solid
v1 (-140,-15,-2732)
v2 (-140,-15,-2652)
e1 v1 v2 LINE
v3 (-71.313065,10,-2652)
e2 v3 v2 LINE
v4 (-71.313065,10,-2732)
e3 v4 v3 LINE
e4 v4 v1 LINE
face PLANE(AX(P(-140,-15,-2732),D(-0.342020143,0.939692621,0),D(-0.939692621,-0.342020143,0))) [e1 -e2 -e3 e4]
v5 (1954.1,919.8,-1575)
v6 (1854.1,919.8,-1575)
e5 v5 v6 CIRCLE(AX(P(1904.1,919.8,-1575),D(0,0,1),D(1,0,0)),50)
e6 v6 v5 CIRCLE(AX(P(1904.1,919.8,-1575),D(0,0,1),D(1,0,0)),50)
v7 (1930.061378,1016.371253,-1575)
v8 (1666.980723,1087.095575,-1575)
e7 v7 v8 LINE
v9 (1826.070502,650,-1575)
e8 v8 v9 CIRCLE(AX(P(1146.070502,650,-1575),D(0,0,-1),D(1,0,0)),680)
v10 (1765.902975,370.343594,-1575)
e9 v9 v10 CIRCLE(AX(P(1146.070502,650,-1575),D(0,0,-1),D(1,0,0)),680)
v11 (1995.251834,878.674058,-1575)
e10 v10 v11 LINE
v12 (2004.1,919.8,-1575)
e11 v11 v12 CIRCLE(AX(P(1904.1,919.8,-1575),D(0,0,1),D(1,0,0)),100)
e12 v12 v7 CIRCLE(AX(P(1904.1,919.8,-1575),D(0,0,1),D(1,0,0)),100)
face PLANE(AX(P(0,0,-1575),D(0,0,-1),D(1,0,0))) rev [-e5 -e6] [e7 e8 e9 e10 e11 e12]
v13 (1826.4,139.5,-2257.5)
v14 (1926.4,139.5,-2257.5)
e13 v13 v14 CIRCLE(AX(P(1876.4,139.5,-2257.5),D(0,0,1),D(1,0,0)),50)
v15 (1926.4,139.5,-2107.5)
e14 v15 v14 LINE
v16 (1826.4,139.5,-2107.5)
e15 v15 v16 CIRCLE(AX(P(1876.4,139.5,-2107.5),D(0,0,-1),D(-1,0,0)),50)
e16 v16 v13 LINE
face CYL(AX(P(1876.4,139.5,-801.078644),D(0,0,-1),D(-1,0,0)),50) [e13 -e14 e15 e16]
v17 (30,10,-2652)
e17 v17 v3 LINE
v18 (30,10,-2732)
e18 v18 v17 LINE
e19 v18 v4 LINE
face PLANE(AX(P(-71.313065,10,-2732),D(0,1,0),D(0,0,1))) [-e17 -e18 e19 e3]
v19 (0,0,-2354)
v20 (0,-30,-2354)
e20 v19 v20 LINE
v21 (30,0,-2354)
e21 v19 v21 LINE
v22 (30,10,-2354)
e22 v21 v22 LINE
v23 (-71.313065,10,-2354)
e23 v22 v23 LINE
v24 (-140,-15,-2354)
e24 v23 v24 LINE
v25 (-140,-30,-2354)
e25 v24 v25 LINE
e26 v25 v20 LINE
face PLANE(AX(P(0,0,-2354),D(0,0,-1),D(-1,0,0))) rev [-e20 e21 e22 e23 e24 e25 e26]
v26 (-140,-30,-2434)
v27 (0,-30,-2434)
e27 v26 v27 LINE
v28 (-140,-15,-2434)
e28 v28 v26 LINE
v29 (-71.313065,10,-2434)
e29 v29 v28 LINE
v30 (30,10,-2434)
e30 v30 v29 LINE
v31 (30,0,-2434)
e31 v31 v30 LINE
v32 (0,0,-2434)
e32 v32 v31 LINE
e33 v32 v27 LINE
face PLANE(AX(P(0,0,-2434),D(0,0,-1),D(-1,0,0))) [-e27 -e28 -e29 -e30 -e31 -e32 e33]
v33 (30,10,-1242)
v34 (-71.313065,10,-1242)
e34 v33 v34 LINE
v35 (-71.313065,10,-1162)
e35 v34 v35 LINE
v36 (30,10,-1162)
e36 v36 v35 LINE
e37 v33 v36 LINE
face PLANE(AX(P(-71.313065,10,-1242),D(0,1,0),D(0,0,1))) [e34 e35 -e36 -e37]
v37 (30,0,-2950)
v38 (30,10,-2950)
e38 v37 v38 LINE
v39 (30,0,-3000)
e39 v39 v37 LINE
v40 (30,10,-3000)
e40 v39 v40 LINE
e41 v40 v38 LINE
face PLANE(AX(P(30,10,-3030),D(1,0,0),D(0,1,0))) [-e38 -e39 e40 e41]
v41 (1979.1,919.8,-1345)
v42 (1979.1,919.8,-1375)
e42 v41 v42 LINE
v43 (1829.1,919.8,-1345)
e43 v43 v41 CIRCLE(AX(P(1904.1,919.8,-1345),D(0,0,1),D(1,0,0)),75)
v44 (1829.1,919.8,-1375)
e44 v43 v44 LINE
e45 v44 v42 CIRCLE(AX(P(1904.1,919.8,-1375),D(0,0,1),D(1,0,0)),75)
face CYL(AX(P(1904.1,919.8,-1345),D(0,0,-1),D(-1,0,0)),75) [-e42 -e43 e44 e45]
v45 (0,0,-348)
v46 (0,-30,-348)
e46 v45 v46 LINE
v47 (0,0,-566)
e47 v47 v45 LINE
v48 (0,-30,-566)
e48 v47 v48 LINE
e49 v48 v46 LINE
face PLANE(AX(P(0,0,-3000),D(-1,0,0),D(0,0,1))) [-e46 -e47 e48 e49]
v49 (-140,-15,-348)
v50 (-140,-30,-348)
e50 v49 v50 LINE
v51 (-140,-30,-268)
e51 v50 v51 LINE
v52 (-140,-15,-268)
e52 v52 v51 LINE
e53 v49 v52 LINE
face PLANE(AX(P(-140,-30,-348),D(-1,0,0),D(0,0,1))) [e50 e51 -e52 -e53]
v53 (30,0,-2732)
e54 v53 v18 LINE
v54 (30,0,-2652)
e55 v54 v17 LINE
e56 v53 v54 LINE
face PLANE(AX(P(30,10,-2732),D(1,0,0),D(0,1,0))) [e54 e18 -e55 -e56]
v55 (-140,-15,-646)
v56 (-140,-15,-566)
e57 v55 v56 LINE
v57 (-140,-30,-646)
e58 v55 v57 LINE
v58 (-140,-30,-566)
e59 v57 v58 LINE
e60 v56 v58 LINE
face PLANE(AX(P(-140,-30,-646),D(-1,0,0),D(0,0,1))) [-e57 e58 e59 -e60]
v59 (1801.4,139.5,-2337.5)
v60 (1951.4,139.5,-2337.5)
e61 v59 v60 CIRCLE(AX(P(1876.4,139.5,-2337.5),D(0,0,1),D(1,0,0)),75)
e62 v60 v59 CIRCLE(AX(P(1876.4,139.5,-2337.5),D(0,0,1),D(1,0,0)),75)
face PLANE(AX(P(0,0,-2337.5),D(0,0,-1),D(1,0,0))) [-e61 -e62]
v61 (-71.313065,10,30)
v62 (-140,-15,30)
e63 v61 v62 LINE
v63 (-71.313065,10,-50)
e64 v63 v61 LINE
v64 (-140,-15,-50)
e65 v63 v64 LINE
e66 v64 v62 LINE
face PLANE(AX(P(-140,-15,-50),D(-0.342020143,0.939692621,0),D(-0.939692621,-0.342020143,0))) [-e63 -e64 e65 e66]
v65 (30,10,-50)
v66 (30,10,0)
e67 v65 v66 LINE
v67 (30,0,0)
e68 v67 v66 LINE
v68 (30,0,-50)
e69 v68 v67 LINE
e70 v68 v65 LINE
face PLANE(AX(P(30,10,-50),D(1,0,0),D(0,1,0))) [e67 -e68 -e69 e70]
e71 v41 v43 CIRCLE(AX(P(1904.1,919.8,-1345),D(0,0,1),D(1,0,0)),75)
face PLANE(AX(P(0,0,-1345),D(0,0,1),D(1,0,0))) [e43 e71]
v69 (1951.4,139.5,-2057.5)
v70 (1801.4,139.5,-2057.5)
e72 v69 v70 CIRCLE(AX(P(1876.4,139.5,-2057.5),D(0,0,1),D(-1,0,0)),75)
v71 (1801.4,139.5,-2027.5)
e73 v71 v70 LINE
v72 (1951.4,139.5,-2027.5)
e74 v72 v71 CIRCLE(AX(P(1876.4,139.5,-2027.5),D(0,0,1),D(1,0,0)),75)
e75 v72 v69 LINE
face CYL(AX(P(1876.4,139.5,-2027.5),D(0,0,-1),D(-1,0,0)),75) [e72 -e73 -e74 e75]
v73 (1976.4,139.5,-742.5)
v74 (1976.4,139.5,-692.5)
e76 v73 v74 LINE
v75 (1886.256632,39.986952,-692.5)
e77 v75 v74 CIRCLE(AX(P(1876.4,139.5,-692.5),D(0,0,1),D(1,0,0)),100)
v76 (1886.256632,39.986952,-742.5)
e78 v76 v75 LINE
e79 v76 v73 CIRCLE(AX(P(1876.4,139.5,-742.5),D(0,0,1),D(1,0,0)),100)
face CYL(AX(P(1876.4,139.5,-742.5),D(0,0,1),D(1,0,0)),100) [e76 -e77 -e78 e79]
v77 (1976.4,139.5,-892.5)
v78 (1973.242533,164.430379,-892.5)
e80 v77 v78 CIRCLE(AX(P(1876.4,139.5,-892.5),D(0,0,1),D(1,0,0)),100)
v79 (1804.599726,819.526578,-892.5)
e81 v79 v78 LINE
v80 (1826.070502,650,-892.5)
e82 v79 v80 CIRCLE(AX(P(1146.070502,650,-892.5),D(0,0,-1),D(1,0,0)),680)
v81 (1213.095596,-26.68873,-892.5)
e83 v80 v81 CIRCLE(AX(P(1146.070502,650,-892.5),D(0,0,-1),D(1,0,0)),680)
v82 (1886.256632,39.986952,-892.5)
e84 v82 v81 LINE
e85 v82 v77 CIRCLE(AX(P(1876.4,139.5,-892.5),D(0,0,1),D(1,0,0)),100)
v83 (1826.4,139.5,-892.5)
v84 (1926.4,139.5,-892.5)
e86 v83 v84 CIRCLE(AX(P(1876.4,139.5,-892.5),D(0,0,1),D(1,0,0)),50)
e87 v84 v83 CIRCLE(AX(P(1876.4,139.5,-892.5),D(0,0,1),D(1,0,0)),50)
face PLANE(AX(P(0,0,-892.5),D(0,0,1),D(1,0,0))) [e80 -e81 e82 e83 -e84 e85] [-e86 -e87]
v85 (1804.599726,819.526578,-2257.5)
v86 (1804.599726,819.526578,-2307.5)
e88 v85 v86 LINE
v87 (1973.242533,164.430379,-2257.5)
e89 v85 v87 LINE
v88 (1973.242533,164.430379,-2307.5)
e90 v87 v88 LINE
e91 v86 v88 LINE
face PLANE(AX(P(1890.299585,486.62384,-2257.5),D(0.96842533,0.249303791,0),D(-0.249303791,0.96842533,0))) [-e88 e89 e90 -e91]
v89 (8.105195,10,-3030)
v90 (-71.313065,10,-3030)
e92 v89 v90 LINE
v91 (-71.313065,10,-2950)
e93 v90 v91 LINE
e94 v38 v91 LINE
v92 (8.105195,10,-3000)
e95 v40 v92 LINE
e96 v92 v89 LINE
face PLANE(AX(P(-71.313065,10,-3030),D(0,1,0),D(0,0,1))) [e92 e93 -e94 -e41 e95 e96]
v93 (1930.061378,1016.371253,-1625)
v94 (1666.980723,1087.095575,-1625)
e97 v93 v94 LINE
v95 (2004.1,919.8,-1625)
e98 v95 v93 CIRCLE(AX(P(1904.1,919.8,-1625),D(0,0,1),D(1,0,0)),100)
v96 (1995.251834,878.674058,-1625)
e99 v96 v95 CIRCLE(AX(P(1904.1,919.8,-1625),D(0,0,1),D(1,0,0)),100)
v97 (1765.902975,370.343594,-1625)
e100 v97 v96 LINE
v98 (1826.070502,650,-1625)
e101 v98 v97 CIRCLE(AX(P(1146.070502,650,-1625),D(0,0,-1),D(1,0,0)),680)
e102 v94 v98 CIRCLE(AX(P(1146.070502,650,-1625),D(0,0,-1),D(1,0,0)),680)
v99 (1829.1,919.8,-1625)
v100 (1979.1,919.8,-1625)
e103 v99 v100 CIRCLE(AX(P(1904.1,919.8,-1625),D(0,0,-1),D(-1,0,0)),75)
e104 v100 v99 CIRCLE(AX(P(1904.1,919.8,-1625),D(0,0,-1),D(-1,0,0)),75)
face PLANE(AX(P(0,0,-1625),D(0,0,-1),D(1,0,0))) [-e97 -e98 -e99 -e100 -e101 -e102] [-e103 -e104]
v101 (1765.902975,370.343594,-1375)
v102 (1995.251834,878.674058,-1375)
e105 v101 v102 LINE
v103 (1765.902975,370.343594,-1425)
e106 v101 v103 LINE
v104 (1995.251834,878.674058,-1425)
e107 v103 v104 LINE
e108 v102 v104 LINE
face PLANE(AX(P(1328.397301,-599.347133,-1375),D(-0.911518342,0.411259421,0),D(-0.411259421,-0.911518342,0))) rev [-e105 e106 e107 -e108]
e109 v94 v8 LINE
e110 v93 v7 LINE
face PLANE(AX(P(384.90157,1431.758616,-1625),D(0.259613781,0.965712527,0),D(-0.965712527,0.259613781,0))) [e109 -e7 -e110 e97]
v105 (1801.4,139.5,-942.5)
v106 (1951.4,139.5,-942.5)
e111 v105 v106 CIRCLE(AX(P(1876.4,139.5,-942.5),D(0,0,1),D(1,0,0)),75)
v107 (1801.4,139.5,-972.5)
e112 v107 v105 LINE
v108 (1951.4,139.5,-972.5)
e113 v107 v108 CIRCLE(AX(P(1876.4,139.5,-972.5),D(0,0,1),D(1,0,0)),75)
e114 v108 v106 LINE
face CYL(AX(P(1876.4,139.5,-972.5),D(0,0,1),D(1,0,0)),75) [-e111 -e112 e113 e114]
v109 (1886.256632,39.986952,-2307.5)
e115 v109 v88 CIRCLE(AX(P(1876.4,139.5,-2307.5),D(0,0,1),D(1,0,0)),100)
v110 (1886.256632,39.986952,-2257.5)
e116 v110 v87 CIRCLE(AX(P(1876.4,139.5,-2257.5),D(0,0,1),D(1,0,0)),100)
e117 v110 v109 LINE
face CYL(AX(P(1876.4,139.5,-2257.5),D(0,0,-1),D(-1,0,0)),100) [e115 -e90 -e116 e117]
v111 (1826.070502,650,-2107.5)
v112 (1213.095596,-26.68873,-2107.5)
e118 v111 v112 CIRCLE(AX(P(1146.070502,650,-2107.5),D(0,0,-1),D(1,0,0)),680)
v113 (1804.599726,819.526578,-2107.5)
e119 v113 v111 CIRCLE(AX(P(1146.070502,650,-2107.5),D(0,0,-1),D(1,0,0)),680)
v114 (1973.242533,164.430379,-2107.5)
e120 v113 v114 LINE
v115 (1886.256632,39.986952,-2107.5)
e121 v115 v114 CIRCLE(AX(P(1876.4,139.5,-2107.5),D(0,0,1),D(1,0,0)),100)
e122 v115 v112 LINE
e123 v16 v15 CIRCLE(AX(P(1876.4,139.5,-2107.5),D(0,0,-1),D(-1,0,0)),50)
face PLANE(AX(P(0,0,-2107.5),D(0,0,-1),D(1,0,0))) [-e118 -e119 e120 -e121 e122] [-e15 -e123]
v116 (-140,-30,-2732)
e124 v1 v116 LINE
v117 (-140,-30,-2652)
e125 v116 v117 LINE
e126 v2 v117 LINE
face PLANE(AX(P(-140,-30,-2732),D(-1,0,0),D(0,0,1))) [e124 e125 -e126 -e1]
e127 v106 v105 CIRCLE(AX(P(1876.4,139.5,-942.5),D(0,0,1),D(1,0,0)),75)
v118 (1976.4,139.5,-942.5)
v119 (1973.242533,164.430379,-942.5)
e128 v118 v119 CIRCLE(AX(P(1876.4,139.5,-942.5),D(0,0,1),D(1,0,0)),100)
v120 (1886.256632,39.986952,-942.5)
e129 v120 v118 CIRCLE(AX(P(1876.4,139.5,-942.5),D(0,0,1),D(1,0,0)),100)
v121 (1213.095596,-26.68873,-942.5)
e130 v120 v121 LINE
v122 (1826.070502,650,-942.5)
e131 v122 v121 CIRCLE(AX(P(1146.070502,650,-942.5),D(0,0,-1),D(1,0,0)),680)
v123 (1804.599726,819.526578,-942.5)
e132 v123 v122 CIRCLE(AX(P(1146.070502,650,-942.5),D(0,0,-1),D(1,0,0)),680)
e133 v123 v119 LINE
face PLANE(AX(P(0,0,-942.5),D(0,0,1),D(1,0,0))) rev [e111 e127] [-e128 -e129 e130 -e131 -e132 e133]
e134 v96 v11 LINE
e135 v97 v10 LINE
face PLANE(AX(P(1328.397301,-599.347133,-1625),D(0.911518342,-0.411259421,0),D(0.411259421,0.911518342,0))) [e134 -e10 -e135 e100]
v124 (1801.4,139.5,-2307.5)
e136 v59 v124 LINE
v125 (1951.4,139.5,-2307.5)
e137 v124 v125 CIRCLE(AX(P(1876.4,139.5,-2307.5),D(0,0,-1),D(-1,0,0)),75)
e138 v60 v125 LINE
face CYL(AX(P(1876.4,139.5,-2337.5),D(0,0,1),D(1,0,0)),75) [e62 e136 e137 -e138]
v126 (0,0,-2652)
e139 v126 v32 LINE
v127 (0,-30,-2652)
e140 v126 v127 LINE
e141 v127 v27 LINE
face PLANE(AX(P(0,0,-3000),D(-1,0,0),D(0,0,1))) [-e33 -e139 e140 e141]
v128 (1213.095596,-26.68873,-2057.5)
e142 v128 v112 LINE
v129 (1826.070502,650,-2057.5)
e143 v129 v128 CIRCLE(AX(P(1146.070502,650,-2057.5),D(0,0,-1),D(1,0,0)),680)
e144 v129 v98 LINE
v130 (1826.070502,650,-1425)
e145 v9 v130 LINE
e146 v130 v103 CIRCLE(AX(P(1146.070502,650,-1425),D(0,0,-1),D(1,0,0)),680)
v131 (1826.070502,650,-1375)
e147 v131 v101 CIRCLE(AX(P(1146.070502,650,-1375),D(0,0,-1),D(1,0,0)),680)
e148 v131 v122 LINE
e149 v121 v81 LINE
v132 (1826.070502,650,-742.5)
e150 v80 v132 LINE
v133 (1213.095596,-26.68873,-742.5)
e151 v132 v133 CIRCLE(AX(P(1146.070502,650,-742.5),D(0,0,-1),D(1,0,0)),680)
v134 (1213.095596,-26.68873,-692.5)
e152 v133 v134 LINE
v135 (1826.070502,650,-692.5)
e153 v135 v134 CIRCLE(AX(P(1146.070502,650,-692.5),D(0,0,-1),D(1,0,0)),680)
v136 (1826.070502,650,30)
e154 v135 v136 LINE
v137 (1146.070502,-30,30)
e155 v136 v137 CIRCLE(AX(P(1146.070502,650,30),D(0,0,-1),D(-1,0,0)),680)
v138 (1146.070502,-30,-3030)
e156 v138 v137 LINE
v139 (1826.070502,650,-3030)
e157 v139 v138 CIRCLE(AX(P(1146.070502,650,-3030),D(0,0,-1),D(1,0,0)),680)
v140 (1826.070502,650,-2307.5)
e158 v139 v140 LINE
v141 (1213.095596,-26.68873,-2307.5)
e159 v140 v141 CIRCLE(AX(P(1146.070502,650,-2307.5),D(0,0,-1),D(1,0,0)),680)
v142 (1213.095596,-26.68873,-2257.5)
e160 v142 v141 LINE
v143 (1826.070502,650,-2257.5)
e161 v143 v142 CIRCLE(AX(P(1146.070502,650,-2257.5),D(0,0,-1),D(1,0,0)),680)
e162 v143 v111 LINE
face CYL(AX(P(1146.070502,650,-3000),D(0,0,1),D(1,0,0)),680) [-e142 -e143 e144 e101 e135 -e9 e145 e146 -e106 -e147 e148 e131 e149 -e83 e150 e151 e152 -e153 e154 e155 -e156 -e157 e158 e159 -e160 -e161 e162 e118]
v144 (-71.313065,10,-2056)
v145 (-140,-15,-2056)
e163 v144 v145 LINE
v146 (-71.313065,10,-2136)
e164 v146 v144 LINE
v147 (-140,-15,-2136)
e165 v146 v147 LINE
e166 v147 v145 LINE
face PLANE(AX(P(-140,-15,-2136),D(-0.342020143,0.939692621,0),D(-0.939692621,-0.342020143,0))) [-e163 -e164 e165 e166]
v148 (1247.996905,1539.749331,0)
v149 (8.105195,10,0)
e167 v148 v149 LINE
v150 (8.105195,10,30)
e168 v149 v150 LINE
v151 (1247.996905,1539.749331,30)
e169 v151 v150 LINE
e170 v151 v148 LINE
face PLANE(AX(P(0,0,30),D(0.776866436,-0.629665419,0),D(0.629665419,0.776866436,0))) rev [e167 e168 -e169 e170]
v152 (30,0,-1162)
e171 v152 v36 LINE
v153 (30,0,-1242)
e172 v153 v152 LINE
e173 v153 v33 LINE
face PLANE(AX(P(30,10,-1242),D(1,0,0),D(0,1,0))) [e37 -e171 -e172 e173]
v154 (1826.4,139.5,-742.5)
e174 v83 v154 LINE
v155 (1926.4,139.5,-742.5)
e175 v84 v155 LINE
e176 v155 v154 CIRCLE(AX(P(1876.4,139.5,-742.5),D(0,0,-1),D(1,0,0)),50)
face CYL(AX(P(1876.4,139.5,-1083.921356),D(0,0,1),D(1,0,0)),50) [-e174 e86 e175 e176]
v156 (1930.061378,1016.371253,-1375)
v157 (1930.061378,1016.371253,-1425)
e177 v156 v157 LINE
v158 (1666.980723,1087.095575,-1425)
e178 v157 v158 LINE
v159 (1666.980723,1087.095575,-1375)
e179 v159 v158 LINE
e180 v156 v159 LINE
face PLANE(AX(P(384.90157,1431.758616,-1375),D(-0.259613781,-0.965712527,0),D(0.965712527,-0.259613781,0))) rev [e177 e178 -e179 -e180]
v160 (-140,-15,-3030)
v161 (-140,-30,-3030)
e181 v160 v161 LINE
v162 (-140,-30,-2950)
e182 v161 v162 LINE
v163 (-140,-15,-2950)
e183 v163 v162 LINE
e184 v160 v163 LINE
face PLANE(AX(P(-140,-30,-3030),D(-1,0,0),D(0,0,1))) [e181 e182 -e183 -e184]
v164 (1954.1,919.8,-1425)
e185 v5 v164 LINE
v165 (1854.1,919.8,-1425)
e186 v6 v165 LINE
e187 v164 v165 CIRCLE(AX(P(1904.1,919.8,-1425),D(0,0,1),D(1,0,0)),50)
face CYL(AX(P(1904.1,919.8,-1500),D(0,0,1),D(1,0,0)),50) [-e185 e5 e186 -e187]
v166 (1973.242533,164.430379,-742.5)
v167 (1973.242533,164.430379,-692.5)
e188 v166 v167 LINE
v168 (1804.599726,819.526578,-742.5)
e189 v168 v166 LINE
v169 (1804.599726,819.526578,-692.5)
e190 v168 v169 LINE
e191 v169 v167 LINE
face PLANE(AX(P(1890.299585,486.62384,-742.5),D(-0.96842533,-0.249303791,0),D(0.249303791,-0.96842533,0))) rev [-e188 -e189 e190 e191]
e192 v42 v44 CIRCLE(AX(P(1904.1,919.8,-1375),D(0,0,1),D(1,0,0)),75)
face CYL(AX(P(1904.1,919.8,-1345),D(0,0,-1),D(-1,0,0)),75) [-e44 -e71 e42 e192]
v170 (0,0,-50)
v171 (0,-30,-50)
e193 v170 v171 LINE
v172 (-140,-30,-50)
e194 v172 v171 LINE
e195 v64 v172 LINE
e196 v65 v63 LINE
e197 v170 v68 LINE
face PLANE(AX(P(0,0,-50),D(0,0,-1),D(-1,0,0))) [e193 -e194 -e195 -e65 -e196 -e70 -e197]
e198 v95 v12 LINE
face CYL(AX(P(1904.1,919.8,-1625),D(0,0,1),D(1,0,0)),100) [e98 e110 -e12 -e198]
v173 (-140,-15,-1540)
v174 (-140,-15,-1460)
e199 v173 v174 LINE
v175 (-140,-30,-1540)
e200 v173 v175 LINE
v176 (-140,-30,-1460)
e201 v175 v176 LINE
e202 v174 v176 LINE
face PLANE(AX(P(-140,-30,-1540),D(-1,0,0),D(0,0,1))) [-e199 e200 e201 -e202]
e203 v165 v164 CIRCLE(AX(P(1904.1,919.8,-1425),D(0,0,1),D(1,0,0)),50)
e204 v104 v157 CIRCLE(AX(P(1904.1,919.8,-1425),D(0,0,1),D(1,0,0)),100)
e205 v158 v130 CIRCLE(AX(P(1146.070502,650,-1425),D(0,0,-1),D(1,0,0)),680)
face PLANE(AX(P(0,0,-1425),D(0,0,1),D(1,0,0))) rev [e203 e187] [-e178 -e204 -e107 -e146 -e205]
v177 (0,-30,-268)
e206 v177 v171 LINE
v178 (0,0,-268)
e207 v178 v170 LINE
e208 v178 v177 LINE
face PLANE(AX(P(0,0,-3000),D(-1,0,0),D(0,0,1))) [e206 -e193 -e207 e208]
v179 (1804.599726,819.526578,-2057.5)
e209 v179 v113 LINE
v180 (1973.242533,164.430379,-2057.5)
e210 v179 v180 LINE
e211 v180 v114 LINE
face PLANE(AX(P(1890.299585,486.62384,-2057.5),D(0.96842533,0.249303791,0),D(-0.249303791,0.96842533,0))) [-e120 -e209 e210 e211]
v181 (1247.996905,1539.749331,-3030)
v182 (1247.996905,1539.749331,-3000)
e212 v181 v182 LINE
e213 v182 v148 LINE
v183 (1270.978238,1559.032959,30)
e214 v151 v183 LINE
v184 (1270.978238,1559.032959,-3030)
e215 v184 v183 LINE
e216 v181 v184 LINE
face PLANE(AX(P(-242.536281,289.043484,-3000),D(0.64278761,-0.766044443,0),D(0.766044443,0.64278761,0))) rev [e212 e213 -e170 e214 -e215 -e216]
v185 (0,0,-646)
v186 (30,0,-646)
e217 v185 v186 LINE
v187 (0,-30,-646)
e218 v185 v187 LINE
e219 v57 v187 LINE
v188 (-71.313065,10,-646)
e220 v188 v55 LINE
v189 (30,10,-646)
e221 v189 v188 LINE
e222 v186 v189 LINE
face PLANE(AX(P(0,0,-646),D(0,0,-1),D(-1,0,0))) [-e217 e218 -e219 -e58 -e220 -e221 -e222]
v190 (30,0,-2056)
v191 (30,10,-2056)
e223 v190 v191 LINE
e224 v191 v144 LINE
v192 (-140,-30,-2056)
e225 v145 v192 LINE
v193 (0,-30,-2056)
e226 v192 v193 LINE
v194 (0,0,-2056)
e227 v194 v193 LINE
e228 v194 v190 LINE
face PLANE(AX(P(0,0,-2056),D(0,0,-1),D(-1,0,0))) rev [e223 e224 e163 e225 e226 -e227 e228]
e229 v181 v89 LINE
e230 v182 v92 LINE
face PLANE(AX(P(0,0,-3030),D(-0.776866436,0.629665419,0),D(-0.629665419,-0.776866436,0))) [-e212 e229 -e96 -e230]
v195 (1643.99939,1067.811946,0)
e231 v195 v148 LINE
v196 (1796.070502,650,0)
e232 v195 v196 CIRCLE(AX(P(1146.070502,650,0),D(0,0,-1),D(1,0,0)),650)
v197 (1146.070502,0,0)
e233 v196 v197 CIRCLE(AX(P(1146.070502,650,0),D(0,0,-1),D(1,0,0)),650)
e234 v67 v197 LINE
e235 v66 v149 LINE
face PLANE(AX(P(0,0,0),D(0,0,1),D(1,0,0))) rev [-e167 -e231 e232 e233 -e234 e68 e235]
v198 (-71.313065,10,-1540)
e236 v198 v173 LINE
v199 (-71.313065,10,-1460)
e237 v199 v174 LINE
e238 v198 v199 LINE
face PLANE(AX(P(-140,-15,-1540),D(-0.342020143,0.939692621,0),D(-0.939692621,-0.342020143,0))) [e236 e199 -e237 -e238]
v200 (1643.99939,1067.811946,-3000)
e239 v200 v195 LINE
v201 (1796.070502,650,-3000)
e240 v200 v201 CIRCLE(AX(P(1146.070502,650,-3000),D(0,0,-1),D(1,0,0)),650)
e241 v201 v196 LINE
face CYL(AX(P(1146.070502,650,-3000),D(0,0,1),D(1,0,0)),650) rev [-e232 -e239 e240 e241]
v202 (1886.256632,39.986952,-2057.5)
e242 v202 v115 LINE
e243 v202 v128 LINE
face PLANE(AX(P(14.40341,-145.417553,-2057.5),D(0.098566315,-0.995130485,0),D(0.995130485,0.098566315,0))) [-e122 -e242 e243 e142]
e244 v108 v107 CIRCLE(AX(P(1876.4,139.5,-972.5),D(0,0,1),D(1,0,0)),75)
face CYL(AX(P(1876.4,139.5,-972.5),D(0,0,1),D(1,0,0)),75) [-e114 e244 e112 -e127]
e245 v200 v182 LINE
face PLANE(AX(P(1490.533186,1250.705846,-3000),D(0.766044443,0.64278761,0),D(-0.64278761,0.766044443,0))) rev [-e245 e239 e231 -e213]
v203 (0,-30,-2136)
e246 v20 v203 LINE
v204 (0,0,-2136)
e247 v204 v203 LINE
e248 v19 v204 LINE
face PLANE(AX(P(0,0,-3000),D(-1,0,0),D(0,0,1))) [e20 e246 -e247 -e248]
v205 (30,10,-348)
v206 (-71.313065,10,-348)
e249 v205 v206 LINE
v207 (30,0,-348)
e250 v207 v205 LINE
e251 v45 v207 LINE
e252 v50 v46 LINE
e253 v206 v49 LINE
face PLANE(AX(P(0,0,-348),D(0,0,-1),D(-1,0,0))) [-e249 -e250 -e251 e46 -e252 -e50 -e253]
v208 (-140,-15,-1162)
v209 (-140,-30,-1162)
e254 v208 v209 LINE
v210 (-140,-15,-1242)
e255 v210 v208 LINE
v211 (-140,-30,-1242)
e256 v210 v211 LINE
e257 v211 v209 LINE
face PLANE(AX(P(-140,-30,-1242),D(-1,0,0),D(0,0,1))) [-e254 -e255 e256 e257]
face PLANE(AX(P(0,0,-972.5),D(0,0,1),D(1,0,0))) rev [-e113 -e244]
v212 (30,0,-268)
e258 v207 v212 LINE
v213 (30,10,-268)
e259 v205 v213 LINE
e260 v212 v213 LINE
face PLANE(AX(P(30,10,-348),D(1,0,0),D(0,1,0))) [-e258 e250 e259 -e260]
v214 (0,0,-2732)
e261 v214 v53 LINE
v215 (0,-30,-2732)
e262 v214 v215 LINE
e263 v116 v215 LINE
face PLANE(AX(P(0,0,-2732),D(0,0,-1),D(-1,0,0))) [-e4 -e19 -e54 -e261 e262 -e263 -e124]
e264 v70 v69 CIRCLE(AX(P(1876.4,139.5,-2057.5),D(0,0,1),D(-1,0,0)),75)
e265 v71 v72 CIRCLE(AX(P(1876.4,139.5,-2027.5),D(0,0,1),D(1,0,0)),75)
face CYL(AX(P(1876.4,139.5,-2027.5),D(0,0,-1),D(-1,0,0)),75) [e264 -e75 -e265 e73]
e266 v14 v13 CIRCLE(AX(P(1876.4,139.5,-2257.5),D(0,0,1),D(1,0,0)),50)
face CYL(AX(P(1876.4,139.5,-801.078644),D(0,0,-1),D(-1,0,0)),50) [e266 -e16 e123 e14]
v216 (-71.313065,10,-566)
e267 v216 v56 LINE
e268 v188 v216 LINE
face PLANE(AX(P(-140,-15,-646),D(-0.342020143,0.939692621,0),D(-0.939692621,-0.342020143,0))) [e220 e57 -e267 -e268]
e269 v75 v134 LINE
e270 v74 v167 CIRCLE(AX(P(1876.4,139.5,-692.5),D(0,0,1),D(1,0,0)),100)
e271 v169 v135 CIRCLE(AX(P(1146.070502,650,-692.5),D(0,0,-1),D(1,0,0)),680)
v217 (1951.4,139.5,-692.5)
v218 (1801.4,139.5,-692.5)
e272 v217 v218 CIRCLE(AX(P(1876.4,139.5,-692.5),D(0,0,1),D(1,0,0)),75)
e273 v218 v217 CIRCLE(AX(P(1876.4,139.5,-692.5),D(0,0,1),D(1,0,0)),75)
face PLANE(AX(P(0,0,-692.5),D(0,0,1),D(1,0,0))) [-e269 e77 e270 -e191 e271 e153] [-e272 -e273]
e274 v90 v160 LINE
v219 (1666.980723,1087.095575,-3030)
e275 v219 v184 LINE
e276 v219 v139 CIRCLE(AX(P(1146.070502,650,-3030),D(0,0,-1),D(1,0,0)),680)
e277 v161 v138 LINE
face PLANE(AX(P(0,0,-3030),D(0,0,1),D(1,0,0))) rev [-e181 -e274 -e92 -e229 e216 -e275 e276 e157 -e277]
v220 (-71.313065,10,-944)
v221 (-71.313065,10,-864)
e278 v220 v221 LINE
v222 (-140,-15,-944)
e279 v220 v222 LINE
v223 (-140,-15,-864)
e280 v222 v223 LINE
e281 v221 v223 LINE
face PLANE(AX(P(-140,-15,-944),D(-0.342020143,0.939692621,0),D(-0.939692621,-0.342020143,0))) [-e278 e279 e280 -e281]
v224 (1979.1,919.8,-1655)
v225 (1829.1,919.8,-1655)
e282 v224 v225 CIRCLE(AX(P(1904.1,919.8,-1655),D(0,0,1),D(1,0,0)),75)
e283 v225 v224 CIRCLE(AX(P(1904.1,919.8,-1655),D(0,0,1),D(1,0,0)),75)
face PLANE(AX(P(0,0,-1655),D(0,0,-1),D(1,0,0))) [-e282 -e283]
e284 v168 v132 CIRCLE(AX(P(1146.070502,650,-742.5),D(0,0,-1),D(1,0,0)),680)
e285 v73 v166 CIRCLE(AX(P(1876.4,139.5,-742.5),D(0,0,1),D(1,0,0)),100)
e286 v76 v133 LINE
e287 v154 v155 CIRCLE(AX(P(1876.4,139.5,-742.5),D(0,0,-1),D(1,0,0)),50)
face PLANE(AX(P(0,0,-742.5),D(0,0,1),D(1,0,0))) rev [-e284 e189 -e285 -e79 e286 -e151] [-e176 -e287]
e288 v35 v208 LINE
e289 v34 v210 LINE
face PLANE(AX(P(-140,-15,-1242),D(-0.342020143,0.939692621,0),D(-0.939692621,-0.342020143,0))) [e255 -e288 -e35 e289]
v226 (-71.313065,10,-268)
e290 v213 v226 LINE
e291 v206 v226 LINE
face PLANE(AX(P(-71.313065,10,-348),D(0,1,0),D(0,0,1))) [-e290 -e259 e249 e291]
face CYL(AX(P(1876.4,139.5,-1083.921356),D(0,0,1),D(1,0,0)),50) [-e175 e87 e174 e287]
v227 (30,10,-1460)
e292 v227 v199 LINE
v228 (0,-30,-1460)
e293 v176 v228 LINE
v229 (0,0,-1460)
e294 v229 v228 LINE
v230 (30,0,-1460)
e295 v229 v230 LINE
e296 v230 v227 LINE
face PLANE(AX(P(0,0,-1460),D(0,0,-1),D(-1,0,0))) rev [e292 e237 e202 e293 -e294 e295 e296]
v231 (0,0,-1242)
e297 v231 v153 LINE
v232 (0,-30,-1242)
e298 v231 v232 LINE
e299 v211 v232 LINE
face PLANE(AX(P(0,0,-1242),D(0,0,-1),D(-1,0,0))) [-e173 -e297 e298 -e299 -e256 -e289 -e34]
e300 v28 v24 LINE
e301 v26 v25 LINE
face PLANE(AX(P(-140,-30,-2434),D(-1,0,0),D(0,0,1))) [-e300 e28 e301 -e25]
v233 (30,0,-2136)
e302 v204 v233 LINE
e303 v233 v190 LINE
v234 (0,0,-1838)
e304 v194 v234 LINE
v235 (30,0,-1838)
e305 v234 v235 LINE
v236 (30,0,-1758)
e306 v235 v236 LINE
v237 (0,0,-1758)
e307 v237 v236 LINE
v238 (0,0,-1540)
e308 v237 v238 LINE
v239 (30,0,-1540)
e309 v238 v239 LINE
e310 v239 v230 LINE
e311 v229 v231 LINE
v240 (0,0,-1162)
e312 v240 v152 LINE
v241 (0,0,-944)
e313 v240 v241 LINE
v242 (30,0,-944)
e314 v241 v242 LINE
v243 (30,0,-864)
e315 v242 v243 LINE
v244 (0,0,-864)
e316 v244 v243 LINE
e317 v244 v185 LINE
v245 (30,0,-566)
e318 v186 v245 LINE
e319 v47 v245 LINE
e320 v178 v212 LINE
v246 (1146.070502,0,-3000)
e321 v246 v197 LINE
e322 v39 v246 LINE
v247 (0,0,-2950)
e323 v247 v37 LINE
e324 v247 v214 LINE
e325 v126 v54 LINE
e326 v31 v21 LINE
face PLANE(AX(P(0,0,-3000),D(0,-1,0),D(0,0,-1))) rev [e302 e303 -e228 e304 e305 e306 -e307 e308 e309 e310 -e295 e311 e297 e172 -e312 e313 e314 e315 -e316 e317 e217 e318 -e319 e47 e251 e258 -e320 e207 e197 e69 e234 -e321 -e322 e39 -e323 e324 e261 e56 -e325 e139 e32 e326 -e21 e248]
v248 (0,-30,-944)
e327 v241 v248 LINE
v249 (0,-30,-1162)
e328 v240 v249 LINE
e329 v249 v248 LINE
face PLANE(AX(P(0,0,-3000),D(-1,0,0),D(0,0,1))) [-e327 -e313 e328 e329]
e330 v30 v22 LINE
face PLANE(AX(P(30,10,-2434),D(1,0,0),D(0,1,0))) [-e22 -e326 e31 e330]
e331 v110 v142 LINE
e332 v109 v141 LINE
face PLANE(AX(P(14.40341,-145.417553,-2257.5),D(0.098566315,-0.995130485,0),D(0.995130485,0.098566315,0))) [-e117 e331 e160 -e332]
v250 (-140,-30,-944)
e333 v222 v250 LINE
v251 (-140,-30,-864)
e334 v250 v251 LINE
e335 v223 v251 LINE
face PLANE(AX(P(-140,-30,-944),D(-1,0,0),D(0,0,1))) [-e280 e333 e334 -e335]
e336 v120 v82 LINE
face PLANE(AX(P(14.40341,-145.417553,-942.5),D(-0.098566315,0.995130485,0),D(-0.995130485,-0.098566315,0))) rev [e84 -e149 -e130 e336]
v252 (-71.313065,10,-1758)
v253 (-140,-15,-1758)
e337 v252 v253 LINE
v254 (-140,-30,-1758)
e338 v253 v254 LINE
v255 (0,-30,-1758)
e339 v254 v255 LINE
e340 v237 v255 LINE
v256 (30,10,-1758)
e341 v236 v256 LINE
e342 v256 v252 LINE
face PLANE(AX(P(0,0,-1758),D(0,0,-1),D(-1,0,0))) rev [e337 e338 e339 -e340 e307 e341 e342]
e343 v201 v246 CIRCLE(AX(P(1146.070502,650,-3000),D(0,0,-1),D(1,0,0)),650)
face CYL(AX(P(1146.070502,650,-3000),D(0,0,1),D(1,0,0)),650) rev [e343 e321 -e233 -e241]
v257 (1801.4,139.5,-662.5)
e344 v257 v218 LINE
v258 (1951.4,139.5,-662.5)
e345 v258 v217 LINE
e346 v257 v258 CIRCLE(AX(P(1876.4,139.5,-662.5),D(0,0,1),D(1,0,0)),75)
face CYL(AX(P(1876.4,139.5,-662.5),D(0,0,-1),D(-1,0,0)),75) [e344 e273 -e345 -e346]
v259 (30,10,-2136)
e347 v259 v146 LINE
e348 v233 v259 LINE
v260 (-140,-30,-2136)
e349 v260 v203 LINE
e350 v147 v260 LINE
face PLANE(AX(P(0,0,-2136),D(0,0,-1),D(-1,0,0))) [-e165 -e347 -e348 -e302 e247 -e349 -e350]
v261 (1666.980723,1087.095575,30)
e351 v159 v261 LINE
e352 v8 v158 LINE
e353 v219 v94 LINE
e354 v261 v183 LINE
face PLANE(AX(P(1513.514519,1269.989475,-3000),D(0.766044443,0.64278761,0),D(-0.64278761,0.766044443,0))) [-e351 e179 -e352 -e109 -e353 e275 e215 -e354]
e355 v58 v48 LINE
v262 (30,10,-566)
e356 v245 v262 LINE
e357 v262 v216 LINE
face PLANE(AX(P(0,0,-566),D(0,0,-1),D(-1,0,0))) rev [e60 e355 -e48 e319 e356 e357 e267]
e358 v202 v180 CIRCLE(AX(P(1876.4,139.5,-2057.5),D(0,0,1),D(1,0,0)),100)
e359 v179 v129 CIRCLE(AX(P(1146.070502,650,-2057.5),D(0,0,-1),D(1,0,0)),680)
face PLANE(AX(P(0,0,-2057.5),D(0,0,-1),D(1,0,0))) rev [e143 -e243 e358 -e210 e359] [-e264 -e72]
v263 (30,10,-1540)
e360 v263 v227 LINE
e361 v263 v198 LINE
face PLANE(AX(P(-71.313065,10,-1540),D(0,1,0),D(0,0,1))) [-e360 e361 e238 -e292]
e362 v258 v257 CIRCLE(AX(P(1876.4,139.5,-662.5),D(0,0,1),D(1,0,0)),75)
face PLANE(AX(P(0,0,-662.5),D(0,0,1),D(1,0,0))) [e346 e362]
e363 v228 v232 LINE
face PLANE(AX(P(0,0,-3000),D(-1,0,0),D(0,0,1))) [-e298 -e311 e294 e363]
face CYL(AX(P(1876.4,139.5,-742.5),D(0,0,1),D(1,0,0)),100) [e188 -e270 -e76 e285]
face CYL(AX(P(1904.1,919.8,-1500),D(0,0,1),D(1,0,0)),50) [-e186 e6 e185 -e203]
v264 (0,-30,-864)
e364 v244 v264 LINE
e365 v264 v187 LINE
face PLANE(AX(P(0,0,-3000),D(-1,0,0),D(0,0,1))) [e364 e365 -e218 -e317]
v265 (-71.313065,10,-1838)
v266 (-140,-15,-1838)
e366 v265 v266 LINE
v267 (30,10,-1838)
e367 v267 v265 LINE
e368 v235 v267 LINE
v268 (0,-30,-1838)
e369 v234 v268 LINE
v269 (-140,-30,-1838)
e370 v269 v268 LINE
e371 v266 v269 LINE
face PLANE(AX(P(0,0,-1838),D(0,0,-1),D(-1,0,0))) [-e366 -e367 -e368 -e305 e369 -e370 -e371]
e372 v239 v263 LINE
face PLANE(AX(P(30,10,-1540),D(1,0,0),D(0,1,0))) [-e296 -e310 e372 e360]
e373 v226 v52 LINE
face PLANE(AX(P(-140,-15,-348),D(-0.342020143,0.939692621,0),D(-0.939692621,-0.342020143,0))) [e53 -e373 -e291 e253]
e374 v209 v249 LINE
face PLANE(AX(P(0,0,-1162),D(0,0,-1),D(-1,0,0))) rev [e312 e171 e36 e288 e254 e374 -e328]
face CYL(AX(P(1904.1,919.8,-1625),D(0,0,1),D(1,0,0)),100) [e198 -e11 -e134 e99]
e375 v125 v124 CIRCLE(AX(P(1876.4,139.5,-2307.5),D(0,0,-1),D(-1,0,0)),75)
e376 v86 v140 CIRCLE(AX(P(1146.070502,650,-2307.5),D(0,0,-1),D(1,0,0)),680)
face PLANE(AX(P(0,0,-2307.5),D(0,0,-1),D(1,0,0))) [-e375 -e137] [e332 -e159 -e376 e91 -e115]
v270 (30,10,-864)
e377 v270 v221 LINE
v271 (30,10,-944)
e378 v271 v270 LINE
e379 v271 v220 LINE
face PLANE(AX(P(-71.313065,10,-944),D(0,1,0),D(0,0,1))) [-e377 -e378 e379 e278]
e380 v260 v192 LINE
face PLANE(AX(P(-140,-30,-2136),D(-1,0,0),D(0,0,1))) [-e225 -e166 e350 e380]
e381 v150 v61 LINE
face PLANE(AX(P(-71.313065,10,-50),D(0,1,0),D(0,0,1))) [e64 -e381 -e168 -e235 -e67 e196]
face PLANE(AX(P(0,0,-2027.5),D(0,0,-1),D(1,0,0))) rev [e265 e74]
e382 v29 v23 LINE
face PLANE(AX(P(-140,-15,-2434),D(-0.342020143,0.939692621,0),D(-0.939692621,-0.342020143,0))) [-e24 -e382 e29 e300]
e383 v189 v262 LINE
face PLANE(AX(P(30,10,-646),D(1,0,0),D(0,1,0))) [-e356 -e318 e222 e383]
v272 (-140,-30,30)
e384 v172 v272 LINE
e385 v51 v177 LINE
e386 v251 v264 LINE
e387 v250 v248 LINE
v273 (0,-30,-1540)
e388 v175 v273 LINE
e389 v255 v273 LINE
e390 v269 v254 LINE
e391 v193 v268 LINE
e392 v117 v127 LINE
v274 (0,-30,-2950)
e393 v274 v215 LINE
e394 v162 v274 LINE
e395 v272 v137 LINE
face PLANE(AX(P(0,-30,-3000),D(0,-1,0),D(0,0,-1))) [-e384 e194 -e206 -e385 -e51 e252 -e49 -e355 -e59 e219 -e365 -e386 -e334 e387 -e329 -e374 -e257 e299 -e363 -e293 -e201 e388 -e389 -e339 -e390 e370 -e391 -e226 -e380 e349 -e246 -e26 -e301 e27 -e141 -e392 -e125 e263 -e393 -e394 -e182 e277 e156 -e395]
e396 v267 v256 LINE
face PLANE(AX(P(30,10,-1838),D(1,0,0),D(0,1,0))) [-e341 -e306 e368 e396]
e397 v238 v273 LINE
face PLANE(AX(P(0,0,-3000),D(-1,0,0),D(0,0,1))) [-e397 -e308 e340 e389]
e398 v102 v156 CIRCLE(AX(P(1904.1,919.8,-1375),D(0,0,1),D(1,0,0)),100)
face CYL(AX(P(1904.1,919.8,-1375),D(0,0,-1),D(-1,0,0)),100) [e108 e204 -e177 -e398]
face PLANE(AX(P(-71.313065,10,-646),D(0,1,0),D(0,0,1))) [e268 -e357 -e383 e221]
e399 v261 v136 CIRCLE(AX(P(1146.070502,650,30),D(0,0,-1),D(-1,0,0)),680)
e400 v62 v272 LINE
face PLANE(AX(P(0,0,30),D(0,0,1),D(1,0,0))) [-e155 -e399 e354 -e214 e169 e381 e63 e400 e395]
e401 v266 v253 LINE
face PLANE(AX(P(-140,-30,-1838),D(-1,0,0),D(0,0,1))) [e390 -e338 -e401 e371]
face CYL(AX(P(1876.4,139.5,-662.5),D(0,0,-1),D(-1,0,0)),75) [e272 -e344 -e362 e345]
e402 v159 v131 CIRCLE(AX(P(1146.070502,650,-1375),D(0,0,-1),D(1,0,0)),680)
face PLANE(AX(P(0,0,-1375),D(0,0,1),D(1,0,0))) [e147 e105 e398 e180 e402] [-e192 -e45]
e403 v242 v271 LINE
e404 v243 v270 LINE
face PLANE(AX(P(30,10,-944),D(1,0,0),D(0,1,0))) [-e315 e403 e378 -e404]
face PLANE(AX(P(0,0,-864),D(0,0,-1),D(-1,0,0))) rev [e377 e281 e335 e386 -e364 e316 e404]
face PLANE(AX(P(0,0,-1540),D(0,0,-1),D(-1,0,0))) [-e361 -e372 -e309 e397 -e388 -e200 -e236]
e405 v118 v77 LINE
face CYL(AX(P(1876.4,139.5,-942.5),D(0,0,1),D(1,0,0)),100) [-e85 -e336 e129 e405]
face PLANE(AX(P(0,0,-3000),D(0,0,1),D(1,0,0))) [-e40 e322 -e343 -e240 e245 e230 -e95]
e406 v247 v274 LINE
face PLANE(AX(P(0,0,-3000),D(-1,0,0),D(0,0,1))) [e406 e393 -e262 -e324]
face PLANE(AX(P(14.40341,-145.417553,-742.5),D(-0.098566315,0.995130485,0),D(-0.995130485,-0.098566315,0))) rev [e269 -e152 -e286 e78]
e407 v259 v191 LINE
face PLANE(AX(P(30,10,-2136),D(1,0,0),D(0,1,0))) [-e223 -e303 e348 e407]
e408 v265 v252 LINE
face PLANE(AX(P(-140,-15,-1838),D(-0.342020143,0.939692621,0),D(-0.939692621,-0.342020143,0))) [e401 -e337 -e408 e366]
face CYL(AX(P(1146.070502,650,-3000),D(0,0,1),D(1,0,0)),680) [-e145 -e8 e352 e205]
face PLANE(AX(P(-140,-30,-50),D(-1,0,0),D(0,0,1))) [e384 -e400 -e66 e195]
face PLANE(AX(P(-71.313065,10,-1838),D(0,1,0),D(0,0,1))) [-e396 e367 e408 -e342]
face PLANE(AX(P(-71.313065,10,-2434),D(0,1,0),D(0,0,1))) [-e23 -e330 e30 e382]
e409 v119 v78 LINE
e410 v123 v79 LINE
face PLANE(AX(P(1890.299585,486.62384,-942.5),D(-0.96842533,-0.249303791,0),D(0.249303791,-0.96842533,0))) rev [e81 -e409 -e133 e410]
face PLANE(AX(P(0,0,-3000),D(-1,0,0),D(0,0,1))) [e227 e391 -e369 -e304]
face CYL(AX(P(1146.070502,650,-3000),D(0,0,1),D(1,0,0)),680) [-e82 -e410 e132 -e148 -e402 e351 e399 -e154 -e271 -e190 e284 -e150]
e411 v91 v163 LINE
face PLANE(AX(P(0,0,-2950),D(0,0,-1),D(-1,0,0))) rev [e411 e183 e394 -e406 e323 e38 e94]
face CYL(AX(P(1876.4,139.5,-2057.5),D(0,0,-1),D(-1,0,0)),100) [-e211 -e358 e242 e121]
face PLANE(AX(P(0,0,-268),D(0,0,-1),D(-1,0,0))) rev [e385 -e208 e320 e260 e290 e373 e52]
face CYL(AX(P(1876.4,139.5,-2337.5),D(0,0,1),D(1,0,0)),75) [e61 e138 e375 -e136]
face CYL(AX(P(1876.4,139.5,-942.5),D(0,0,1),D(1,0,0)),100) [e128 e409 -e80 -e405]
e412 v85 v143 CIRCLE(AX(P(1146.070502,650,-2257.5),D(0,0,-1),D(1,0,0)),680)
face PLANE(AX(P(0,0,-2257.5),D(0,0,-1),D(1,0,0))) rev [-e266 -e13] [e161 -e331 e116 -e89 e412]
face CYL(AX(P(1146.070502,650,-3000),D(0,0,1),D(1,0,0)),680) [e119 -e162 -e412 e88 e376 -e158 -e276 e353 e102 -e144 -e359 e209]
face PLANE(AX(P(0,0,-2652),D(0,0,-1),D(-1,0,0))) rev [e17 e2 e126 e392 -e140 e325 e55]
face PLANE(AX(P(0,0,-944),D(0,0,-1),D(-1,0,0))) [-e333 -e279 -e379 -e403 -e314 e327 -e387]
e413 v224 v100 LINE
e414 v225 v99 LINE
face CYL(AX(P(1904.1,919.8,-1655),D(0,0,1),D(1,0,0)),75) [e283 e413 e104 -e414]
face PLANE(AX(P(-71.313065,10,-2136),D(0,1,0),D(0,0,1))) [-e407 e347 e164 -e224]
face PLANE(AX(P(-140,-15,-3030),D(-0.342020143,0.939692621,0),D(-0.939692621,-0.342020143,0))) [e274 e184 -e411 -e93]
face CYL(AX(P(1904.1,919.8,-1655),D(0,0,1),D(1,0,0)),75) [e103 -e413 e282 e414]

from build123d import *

# Parameters (mm, degrees)
BOSS_EXTRUDE1_DEPTH  = 3000
BOSS_EXTRUDE2_START  = 30
BOSS_EXTRUDE2_DEPTH  = 30
BOSS_EXTRUDE4_START  = -3000
BOSS_EXTRUDE4_DEPTH  = 30
BOSS_EXTRUDE5_START  = -692.5
SKETCH_1_11_R        = 50
BOSS_EXTRUDE5_DEPTH  = 50
BOSS_EXTRUDE6_START  = -892.5
SKETCH_1_12_R        = 50
BOSS_EXTRUDE6_DEPTH  = 50
BOSS_EXTRUDE7_START  = -1375
SKETCH_1_13_2_R      = 50
BOSS_EXTRUDE7_DEPTH  = 50
SKETCH_3_5_R         = 50
BOSS_EXTRUDE8_DEPTH  = 250
BOSS_EXTRUDE9_START  = 30
SKETCH_3_4_R         = 75
SKETCH_3_4_R_2       = 50
BOSS_EXTRUDE9_DEPTH  = 30
BOSS_EXTRUDE10_START = -250
SKETCH_3_5_2_R       = 75
SKETCH_3_5_2_R_2     = 50
BOSS_EXTRUDE10_DEPTH = 30
BOSS_EXTRUDE11_START = 30
SKETCH_4_3_R         = 75
SKETCH_4_3_R_2       = 50
BOSS_EXTRUDE11_DEPTH = 30
SKETCH_4_3_2_R       = 50
BOSS_EXTRUDE12_DEPTH = 125
BOSS_EXTRUDE13_DEPTH = 80
LPATTERN1_COUNT      = 11
LPATTERN1_PITCH      = 298


with BuildPart() as part:
    # Sketch 1_13 → Boss-Extrude1 (new body)
    with BuildSketch(Plane.XY):
        with BuildLine():
            ThreePointArc((1666.98072299, 1087.095574587), (1762.359796854, 362.619582016), (1146.070501669, -30))
            Line((1146.070501669, -30), (0, -30))
            Line((0, -30), (0, 0))
            Line((0, 0), (1146.070501669, 0))
            ThreePointArc((1146.070501669, 0), (1735.170563243, 375.298129869), (1643.999389696, 1067.811946296))
            Line((1643.999389696, 1067.811946296), (1247.99690453, 1539.749330669))
            Line((1247.99690453, 1539.749330669), (1270.978237824, 1559.03295896))
            Line((1270.978237824, 1559.03295896), (1666.98072299, 1087.095574587))
        make_face()
    extrude(amount=-BOSS_EXTRUDE1_DEPTH)

    # 草图1<7> → Boss-Extrude2 (add)
    with BuildSketch(Plane.XY.offset(BOSS_EXTRUDE2_START)):
        with BuildLine():
            Line((1247.99690453, 1539.749330669), (0, 0))
            Line((0, 0), (0, -30))
            Line((0, -30), (1146.070501669, -30))
            ThreePointArc((1146.070501669, -30), (1762.359796854, 362.619582016), (1666.98072299, 1087.095574587))
            Line((1666.98072299, 1087.095574587), (1270.978237824, 1559.03295896))
            Line((1270.978237824, 1559.03295896), (1247.99690453, 1539.749330669))
        make_face()
    extrude(amount=-BOSS_EXTRUDE2_DEPTH)

    # 草图1<9> → Boss-Extrude4 (add)
    with BuildSketch(Plane.XY.offset(BOSS_EXTRUDE4_START)):
        with BuildLine():
            ThreePointArc((1643.999389696, 1067.811946296), (1735.170563243, 375.298129869), (1146.070501669, 0))
            Line((1146.070501669, 0), (0, 0))
            Line((0, 0), (1247.99690453, 1539.749330669))
            Line((1247.99690453, 1539.749330669), (1643.999389696, 1067.811946296))
        make_face()
        with BuildLine():
            ThreePointArc((1666.98072299, 1087.095574587), (1762.359796854, 362.619582016), (1146.070501669, -30))
            Line((1146.070501669, -30), (0, -30))
            Line((0, -30), (0, 0))
            Line((0, 0), (1146.070501669, 0))
            ThreePointArc((1146.070501669, 0), (1735.170563243, 375.298129869), (1643.999389696, 1067.811946296))
            Line((1643.999389696, 1067.811946296), (1247.99690453, 1539.749330669))
            Line((1247.99690453, 1539.749330669), (1270.978237824, 1559.03295896))
            Line((1270.978237824, 1559.03295896), (1666.98072299, 1087.095574587))
        make_face()
    extrude(amount=-BOSS_EXTRUDE4_DEPTH)

    # 草图1<11> → Boss-Extrude5 (add)
    with BuildSketch(Plane.XY.offset(BOSS_EXTRUDE5_START)):
        with BuildLine():
            Line((1213.095596051, -26.688729567), (1886.256631527, 39.986951534))
            ThreePointArc((1886.256631527, 39.986951534), (1958.361695899, 82.208810404), (1973.242532996, 164.430379118))
            Line((1973.242532996, 164.430379118), (1804.599726039, 819.526578004))
            ThreePointArc((1804.599726039, 819.526578004), (1703.410033783, 260.419910747), (1213.095596051, -26.688729567))
        make_face()
        with Locations((1876.4, 139.5)):
            Circle(SKETCH_1_11_R, mode=Mode.SUBTRACT)
    boss_extrude5 = extrude(amount=-BOSS_EXTRUDE5_DEPTH)

    # 草图1<12> → Boss-Extrude6 (add)
    with BuildSketch(Plane.XY.offset(BOSS_EXTRUDE6_START)):
        with BuildLine():
            Line((1213.095596051, -26.688729567), (1886.256631527, 39.986951534))
            ThreePointArc((1886.256631527, 39.986951534), (1958.361695899, 82.208810404), (1973.242532996, 164.430379118))
            Line((1973.242532996, 164.430379118), (1804.599726039, 819.526578004))
            ThreePointArc((1804.599726039, 819.526578004), (1703.410033783, 260.419910747), (1213.095596051, -26.688729567))
        make_face()
        with Locations((1876.4, 139.5)):
            Circle(SKETCH_1_12_R, mode=Mode.SUBTRACT)
    boss_extrude6 = extrude(amount=-BOSS_EXTRUDE6_DEPTH)

    # Sketch 1_13 2 → Boss-Extrude7 (add)
    with BuildSketch(Plane.XY.offset(BOSS_EXTRUDE7_START)):
        with BuildLine():
            Line((1930.061378111, 1016.371252693), (1666.98072299, 1087.095574587))
            ThreePointArc((1666.98072299, 1087.095574587), (1819.685246249, 742.968682279), (1765.902974507, 370.343593645))
            Line((1765.902974507, 370.343593645), (1995.251834241, 878.674057889))
            ThreePointArc((1995.251834241, 878.674057889), (1994.482550811, 962.590121629), (1930.061378111, 1016.371252693))
        make_face()
        with Locations((1904.1, 919.8)):
            Circle(SKETCH_1_13_2_R, mode=Mode.SUBTRACT)
    boss_extrude7 = extrude(amount=-BOSS_EXTRUDE7_DEPTH)

    # Sketch 3_5 → Boss-Extrude8 (add)
    with BuildSketch(Plane.XY.offset(-692.5)):
        with Locations((1876.4, 139.5)):
            Circle(SKETCH_3_5_R)
    boss_extrude8 = extrude(amount=-BOSS_EXTRUDE8_DEPTH)

    # 草图3<4> → Boss-Extrude9 (add)
    # profile 1 of 2: a face of its own
    with BuildSketch(Plane.XY.offset(-692.5).offset(BOSS_EXTRUDE9_START)):
        with Locations((1876.4, 139.5)):
            Circle(SKETCH_3_4_R)
        with Locations((1876.4, 139.5)):
            Circle(SKETCH_3_4_R_2, mode=Mode.SUBTRACT)
    # profile 2 of 2: a face of its own
    with BuildSketch(Plane.XY.offset(-692.5).offset(BOSS_EXTRUDE9_START)):
        with Locations((1876.4, 139.5)):
            Circle(SKETCH_3_4_R_2)
    boss_extrude9 = extrude(amount=-BOSS_EXTRUDE9_DEPTH)

    # Sketch 3_5 2 → Boss-Extrude10 (add)
    # profile 1 of 2: a face of its own
    with BuildSketch(Plane.XY.offset(-692.5).offset(BOSS_EXTRUDE10_START)):
        with Locations((1876.4, 139.5)):
            Circle(SKETCH_3_5_2_R)
        with Locations((1876.4, 139.5)):
            Circle(SKETCH_3_5_2_R_2, mode=Mode.SUBTRACT)
    # profile 2 of 2: a face of its own
    with BuildSketch(Plane.XY.offset(-692.5).offset(BOSS_EXTRUDE10_START)):
        with Locations((1876.4, 139.5)):
            Circle(SKETCH_3_5_2_R_2)
    boss_extrude10 = extrude(amount=-BOSS_EXTRUDE10_DEPTH)

    # Sketch 4_3 → Boss-Extrude11 (add)
    # profile 1 of 2: a face of its own
    with BuildSketch(Plane.XY.offset(-1375).offset(BOSS_EXTRUDE11_START)):
        with Locations((1904.1, 919.8)):
            Circle(SKETCH_4_3_R)
        with Locations((1904.1, 919.8)):
            Circle(SKETCH_4_3_R_2, mode=Mode.SUBTRACT)
    # profile 2 of 2: a face of its own
    with BuildSketch(Plane.XY.offset(-1375).offset(BOSS_EXTRUDE11_START)):
        with Locations((1904.1, 919.8)):
            Circle(SKETCH_4_3_R_2)
    boss_extrude11 = extrude(amount=-BOSS_EXTRUDE11_DEPTH)

    # Sketch 4_3 2 → Boss-Extrude12 (add)
    with BuildSketch(Plane.XY.offset(-1375)):
        with Locations((1904.1, 919.8)):
            Circle(SKETCH_4_3_2_R)
    boss_extrude12 = extrude(amount=-BOSS_EXTRUDE12_DEPTH)

    # Mirror1: Boss-Extrude5, Boss-Extrude6, Boss-Extrude7, Boss-Extrude8, Boss-Extrude9, Boss-Extrude10, Boss-Extrude11, Boss-Extrude12 across plane
    add(boss_extrude5.mirror(Plane.XY.offset(-1500)))
    add(boss_extrude6.mirror(Plane.XY.offset(-1500)))
    add(boss_extrude7.mirror(Plane.XY.offset(-1500)))
    add(boss_extrude8.mirror(Plane.XY.offset(-1500)))
    add(boss_extrude9.mirror(Plane.XY.offset(-1500)))
    add(boss_extrude10.mirror(Plane.XY.offset(-1500)))
    add(boss_extrude11.mirror(Plane.XY.offset(-1500)))
    add(boss_extrude12.mirror(Plane.XY.offset(-1500)))

    # Sketch5 → Boss-Extrude13 (add)
    with BuildSketch(Plane.XY.offset(30)):
        Polygon((0, -30), (-140, -30), (-140, -15), (-71.313064514, 10), (30, 10), (30, -30), align=None)
    boss_extrude13 = extrude(amount=-BOSS_EXTRUDE13_DEPTH)

    # LPattern1: Boss-Extrude13 ×11
    with Locations(*[(0, 0, -i * LPATTERN1_PITCH) for i in range(1, LPATTERN1_COUNT)]):
        add(boss_extrude13)


solid = part.part
